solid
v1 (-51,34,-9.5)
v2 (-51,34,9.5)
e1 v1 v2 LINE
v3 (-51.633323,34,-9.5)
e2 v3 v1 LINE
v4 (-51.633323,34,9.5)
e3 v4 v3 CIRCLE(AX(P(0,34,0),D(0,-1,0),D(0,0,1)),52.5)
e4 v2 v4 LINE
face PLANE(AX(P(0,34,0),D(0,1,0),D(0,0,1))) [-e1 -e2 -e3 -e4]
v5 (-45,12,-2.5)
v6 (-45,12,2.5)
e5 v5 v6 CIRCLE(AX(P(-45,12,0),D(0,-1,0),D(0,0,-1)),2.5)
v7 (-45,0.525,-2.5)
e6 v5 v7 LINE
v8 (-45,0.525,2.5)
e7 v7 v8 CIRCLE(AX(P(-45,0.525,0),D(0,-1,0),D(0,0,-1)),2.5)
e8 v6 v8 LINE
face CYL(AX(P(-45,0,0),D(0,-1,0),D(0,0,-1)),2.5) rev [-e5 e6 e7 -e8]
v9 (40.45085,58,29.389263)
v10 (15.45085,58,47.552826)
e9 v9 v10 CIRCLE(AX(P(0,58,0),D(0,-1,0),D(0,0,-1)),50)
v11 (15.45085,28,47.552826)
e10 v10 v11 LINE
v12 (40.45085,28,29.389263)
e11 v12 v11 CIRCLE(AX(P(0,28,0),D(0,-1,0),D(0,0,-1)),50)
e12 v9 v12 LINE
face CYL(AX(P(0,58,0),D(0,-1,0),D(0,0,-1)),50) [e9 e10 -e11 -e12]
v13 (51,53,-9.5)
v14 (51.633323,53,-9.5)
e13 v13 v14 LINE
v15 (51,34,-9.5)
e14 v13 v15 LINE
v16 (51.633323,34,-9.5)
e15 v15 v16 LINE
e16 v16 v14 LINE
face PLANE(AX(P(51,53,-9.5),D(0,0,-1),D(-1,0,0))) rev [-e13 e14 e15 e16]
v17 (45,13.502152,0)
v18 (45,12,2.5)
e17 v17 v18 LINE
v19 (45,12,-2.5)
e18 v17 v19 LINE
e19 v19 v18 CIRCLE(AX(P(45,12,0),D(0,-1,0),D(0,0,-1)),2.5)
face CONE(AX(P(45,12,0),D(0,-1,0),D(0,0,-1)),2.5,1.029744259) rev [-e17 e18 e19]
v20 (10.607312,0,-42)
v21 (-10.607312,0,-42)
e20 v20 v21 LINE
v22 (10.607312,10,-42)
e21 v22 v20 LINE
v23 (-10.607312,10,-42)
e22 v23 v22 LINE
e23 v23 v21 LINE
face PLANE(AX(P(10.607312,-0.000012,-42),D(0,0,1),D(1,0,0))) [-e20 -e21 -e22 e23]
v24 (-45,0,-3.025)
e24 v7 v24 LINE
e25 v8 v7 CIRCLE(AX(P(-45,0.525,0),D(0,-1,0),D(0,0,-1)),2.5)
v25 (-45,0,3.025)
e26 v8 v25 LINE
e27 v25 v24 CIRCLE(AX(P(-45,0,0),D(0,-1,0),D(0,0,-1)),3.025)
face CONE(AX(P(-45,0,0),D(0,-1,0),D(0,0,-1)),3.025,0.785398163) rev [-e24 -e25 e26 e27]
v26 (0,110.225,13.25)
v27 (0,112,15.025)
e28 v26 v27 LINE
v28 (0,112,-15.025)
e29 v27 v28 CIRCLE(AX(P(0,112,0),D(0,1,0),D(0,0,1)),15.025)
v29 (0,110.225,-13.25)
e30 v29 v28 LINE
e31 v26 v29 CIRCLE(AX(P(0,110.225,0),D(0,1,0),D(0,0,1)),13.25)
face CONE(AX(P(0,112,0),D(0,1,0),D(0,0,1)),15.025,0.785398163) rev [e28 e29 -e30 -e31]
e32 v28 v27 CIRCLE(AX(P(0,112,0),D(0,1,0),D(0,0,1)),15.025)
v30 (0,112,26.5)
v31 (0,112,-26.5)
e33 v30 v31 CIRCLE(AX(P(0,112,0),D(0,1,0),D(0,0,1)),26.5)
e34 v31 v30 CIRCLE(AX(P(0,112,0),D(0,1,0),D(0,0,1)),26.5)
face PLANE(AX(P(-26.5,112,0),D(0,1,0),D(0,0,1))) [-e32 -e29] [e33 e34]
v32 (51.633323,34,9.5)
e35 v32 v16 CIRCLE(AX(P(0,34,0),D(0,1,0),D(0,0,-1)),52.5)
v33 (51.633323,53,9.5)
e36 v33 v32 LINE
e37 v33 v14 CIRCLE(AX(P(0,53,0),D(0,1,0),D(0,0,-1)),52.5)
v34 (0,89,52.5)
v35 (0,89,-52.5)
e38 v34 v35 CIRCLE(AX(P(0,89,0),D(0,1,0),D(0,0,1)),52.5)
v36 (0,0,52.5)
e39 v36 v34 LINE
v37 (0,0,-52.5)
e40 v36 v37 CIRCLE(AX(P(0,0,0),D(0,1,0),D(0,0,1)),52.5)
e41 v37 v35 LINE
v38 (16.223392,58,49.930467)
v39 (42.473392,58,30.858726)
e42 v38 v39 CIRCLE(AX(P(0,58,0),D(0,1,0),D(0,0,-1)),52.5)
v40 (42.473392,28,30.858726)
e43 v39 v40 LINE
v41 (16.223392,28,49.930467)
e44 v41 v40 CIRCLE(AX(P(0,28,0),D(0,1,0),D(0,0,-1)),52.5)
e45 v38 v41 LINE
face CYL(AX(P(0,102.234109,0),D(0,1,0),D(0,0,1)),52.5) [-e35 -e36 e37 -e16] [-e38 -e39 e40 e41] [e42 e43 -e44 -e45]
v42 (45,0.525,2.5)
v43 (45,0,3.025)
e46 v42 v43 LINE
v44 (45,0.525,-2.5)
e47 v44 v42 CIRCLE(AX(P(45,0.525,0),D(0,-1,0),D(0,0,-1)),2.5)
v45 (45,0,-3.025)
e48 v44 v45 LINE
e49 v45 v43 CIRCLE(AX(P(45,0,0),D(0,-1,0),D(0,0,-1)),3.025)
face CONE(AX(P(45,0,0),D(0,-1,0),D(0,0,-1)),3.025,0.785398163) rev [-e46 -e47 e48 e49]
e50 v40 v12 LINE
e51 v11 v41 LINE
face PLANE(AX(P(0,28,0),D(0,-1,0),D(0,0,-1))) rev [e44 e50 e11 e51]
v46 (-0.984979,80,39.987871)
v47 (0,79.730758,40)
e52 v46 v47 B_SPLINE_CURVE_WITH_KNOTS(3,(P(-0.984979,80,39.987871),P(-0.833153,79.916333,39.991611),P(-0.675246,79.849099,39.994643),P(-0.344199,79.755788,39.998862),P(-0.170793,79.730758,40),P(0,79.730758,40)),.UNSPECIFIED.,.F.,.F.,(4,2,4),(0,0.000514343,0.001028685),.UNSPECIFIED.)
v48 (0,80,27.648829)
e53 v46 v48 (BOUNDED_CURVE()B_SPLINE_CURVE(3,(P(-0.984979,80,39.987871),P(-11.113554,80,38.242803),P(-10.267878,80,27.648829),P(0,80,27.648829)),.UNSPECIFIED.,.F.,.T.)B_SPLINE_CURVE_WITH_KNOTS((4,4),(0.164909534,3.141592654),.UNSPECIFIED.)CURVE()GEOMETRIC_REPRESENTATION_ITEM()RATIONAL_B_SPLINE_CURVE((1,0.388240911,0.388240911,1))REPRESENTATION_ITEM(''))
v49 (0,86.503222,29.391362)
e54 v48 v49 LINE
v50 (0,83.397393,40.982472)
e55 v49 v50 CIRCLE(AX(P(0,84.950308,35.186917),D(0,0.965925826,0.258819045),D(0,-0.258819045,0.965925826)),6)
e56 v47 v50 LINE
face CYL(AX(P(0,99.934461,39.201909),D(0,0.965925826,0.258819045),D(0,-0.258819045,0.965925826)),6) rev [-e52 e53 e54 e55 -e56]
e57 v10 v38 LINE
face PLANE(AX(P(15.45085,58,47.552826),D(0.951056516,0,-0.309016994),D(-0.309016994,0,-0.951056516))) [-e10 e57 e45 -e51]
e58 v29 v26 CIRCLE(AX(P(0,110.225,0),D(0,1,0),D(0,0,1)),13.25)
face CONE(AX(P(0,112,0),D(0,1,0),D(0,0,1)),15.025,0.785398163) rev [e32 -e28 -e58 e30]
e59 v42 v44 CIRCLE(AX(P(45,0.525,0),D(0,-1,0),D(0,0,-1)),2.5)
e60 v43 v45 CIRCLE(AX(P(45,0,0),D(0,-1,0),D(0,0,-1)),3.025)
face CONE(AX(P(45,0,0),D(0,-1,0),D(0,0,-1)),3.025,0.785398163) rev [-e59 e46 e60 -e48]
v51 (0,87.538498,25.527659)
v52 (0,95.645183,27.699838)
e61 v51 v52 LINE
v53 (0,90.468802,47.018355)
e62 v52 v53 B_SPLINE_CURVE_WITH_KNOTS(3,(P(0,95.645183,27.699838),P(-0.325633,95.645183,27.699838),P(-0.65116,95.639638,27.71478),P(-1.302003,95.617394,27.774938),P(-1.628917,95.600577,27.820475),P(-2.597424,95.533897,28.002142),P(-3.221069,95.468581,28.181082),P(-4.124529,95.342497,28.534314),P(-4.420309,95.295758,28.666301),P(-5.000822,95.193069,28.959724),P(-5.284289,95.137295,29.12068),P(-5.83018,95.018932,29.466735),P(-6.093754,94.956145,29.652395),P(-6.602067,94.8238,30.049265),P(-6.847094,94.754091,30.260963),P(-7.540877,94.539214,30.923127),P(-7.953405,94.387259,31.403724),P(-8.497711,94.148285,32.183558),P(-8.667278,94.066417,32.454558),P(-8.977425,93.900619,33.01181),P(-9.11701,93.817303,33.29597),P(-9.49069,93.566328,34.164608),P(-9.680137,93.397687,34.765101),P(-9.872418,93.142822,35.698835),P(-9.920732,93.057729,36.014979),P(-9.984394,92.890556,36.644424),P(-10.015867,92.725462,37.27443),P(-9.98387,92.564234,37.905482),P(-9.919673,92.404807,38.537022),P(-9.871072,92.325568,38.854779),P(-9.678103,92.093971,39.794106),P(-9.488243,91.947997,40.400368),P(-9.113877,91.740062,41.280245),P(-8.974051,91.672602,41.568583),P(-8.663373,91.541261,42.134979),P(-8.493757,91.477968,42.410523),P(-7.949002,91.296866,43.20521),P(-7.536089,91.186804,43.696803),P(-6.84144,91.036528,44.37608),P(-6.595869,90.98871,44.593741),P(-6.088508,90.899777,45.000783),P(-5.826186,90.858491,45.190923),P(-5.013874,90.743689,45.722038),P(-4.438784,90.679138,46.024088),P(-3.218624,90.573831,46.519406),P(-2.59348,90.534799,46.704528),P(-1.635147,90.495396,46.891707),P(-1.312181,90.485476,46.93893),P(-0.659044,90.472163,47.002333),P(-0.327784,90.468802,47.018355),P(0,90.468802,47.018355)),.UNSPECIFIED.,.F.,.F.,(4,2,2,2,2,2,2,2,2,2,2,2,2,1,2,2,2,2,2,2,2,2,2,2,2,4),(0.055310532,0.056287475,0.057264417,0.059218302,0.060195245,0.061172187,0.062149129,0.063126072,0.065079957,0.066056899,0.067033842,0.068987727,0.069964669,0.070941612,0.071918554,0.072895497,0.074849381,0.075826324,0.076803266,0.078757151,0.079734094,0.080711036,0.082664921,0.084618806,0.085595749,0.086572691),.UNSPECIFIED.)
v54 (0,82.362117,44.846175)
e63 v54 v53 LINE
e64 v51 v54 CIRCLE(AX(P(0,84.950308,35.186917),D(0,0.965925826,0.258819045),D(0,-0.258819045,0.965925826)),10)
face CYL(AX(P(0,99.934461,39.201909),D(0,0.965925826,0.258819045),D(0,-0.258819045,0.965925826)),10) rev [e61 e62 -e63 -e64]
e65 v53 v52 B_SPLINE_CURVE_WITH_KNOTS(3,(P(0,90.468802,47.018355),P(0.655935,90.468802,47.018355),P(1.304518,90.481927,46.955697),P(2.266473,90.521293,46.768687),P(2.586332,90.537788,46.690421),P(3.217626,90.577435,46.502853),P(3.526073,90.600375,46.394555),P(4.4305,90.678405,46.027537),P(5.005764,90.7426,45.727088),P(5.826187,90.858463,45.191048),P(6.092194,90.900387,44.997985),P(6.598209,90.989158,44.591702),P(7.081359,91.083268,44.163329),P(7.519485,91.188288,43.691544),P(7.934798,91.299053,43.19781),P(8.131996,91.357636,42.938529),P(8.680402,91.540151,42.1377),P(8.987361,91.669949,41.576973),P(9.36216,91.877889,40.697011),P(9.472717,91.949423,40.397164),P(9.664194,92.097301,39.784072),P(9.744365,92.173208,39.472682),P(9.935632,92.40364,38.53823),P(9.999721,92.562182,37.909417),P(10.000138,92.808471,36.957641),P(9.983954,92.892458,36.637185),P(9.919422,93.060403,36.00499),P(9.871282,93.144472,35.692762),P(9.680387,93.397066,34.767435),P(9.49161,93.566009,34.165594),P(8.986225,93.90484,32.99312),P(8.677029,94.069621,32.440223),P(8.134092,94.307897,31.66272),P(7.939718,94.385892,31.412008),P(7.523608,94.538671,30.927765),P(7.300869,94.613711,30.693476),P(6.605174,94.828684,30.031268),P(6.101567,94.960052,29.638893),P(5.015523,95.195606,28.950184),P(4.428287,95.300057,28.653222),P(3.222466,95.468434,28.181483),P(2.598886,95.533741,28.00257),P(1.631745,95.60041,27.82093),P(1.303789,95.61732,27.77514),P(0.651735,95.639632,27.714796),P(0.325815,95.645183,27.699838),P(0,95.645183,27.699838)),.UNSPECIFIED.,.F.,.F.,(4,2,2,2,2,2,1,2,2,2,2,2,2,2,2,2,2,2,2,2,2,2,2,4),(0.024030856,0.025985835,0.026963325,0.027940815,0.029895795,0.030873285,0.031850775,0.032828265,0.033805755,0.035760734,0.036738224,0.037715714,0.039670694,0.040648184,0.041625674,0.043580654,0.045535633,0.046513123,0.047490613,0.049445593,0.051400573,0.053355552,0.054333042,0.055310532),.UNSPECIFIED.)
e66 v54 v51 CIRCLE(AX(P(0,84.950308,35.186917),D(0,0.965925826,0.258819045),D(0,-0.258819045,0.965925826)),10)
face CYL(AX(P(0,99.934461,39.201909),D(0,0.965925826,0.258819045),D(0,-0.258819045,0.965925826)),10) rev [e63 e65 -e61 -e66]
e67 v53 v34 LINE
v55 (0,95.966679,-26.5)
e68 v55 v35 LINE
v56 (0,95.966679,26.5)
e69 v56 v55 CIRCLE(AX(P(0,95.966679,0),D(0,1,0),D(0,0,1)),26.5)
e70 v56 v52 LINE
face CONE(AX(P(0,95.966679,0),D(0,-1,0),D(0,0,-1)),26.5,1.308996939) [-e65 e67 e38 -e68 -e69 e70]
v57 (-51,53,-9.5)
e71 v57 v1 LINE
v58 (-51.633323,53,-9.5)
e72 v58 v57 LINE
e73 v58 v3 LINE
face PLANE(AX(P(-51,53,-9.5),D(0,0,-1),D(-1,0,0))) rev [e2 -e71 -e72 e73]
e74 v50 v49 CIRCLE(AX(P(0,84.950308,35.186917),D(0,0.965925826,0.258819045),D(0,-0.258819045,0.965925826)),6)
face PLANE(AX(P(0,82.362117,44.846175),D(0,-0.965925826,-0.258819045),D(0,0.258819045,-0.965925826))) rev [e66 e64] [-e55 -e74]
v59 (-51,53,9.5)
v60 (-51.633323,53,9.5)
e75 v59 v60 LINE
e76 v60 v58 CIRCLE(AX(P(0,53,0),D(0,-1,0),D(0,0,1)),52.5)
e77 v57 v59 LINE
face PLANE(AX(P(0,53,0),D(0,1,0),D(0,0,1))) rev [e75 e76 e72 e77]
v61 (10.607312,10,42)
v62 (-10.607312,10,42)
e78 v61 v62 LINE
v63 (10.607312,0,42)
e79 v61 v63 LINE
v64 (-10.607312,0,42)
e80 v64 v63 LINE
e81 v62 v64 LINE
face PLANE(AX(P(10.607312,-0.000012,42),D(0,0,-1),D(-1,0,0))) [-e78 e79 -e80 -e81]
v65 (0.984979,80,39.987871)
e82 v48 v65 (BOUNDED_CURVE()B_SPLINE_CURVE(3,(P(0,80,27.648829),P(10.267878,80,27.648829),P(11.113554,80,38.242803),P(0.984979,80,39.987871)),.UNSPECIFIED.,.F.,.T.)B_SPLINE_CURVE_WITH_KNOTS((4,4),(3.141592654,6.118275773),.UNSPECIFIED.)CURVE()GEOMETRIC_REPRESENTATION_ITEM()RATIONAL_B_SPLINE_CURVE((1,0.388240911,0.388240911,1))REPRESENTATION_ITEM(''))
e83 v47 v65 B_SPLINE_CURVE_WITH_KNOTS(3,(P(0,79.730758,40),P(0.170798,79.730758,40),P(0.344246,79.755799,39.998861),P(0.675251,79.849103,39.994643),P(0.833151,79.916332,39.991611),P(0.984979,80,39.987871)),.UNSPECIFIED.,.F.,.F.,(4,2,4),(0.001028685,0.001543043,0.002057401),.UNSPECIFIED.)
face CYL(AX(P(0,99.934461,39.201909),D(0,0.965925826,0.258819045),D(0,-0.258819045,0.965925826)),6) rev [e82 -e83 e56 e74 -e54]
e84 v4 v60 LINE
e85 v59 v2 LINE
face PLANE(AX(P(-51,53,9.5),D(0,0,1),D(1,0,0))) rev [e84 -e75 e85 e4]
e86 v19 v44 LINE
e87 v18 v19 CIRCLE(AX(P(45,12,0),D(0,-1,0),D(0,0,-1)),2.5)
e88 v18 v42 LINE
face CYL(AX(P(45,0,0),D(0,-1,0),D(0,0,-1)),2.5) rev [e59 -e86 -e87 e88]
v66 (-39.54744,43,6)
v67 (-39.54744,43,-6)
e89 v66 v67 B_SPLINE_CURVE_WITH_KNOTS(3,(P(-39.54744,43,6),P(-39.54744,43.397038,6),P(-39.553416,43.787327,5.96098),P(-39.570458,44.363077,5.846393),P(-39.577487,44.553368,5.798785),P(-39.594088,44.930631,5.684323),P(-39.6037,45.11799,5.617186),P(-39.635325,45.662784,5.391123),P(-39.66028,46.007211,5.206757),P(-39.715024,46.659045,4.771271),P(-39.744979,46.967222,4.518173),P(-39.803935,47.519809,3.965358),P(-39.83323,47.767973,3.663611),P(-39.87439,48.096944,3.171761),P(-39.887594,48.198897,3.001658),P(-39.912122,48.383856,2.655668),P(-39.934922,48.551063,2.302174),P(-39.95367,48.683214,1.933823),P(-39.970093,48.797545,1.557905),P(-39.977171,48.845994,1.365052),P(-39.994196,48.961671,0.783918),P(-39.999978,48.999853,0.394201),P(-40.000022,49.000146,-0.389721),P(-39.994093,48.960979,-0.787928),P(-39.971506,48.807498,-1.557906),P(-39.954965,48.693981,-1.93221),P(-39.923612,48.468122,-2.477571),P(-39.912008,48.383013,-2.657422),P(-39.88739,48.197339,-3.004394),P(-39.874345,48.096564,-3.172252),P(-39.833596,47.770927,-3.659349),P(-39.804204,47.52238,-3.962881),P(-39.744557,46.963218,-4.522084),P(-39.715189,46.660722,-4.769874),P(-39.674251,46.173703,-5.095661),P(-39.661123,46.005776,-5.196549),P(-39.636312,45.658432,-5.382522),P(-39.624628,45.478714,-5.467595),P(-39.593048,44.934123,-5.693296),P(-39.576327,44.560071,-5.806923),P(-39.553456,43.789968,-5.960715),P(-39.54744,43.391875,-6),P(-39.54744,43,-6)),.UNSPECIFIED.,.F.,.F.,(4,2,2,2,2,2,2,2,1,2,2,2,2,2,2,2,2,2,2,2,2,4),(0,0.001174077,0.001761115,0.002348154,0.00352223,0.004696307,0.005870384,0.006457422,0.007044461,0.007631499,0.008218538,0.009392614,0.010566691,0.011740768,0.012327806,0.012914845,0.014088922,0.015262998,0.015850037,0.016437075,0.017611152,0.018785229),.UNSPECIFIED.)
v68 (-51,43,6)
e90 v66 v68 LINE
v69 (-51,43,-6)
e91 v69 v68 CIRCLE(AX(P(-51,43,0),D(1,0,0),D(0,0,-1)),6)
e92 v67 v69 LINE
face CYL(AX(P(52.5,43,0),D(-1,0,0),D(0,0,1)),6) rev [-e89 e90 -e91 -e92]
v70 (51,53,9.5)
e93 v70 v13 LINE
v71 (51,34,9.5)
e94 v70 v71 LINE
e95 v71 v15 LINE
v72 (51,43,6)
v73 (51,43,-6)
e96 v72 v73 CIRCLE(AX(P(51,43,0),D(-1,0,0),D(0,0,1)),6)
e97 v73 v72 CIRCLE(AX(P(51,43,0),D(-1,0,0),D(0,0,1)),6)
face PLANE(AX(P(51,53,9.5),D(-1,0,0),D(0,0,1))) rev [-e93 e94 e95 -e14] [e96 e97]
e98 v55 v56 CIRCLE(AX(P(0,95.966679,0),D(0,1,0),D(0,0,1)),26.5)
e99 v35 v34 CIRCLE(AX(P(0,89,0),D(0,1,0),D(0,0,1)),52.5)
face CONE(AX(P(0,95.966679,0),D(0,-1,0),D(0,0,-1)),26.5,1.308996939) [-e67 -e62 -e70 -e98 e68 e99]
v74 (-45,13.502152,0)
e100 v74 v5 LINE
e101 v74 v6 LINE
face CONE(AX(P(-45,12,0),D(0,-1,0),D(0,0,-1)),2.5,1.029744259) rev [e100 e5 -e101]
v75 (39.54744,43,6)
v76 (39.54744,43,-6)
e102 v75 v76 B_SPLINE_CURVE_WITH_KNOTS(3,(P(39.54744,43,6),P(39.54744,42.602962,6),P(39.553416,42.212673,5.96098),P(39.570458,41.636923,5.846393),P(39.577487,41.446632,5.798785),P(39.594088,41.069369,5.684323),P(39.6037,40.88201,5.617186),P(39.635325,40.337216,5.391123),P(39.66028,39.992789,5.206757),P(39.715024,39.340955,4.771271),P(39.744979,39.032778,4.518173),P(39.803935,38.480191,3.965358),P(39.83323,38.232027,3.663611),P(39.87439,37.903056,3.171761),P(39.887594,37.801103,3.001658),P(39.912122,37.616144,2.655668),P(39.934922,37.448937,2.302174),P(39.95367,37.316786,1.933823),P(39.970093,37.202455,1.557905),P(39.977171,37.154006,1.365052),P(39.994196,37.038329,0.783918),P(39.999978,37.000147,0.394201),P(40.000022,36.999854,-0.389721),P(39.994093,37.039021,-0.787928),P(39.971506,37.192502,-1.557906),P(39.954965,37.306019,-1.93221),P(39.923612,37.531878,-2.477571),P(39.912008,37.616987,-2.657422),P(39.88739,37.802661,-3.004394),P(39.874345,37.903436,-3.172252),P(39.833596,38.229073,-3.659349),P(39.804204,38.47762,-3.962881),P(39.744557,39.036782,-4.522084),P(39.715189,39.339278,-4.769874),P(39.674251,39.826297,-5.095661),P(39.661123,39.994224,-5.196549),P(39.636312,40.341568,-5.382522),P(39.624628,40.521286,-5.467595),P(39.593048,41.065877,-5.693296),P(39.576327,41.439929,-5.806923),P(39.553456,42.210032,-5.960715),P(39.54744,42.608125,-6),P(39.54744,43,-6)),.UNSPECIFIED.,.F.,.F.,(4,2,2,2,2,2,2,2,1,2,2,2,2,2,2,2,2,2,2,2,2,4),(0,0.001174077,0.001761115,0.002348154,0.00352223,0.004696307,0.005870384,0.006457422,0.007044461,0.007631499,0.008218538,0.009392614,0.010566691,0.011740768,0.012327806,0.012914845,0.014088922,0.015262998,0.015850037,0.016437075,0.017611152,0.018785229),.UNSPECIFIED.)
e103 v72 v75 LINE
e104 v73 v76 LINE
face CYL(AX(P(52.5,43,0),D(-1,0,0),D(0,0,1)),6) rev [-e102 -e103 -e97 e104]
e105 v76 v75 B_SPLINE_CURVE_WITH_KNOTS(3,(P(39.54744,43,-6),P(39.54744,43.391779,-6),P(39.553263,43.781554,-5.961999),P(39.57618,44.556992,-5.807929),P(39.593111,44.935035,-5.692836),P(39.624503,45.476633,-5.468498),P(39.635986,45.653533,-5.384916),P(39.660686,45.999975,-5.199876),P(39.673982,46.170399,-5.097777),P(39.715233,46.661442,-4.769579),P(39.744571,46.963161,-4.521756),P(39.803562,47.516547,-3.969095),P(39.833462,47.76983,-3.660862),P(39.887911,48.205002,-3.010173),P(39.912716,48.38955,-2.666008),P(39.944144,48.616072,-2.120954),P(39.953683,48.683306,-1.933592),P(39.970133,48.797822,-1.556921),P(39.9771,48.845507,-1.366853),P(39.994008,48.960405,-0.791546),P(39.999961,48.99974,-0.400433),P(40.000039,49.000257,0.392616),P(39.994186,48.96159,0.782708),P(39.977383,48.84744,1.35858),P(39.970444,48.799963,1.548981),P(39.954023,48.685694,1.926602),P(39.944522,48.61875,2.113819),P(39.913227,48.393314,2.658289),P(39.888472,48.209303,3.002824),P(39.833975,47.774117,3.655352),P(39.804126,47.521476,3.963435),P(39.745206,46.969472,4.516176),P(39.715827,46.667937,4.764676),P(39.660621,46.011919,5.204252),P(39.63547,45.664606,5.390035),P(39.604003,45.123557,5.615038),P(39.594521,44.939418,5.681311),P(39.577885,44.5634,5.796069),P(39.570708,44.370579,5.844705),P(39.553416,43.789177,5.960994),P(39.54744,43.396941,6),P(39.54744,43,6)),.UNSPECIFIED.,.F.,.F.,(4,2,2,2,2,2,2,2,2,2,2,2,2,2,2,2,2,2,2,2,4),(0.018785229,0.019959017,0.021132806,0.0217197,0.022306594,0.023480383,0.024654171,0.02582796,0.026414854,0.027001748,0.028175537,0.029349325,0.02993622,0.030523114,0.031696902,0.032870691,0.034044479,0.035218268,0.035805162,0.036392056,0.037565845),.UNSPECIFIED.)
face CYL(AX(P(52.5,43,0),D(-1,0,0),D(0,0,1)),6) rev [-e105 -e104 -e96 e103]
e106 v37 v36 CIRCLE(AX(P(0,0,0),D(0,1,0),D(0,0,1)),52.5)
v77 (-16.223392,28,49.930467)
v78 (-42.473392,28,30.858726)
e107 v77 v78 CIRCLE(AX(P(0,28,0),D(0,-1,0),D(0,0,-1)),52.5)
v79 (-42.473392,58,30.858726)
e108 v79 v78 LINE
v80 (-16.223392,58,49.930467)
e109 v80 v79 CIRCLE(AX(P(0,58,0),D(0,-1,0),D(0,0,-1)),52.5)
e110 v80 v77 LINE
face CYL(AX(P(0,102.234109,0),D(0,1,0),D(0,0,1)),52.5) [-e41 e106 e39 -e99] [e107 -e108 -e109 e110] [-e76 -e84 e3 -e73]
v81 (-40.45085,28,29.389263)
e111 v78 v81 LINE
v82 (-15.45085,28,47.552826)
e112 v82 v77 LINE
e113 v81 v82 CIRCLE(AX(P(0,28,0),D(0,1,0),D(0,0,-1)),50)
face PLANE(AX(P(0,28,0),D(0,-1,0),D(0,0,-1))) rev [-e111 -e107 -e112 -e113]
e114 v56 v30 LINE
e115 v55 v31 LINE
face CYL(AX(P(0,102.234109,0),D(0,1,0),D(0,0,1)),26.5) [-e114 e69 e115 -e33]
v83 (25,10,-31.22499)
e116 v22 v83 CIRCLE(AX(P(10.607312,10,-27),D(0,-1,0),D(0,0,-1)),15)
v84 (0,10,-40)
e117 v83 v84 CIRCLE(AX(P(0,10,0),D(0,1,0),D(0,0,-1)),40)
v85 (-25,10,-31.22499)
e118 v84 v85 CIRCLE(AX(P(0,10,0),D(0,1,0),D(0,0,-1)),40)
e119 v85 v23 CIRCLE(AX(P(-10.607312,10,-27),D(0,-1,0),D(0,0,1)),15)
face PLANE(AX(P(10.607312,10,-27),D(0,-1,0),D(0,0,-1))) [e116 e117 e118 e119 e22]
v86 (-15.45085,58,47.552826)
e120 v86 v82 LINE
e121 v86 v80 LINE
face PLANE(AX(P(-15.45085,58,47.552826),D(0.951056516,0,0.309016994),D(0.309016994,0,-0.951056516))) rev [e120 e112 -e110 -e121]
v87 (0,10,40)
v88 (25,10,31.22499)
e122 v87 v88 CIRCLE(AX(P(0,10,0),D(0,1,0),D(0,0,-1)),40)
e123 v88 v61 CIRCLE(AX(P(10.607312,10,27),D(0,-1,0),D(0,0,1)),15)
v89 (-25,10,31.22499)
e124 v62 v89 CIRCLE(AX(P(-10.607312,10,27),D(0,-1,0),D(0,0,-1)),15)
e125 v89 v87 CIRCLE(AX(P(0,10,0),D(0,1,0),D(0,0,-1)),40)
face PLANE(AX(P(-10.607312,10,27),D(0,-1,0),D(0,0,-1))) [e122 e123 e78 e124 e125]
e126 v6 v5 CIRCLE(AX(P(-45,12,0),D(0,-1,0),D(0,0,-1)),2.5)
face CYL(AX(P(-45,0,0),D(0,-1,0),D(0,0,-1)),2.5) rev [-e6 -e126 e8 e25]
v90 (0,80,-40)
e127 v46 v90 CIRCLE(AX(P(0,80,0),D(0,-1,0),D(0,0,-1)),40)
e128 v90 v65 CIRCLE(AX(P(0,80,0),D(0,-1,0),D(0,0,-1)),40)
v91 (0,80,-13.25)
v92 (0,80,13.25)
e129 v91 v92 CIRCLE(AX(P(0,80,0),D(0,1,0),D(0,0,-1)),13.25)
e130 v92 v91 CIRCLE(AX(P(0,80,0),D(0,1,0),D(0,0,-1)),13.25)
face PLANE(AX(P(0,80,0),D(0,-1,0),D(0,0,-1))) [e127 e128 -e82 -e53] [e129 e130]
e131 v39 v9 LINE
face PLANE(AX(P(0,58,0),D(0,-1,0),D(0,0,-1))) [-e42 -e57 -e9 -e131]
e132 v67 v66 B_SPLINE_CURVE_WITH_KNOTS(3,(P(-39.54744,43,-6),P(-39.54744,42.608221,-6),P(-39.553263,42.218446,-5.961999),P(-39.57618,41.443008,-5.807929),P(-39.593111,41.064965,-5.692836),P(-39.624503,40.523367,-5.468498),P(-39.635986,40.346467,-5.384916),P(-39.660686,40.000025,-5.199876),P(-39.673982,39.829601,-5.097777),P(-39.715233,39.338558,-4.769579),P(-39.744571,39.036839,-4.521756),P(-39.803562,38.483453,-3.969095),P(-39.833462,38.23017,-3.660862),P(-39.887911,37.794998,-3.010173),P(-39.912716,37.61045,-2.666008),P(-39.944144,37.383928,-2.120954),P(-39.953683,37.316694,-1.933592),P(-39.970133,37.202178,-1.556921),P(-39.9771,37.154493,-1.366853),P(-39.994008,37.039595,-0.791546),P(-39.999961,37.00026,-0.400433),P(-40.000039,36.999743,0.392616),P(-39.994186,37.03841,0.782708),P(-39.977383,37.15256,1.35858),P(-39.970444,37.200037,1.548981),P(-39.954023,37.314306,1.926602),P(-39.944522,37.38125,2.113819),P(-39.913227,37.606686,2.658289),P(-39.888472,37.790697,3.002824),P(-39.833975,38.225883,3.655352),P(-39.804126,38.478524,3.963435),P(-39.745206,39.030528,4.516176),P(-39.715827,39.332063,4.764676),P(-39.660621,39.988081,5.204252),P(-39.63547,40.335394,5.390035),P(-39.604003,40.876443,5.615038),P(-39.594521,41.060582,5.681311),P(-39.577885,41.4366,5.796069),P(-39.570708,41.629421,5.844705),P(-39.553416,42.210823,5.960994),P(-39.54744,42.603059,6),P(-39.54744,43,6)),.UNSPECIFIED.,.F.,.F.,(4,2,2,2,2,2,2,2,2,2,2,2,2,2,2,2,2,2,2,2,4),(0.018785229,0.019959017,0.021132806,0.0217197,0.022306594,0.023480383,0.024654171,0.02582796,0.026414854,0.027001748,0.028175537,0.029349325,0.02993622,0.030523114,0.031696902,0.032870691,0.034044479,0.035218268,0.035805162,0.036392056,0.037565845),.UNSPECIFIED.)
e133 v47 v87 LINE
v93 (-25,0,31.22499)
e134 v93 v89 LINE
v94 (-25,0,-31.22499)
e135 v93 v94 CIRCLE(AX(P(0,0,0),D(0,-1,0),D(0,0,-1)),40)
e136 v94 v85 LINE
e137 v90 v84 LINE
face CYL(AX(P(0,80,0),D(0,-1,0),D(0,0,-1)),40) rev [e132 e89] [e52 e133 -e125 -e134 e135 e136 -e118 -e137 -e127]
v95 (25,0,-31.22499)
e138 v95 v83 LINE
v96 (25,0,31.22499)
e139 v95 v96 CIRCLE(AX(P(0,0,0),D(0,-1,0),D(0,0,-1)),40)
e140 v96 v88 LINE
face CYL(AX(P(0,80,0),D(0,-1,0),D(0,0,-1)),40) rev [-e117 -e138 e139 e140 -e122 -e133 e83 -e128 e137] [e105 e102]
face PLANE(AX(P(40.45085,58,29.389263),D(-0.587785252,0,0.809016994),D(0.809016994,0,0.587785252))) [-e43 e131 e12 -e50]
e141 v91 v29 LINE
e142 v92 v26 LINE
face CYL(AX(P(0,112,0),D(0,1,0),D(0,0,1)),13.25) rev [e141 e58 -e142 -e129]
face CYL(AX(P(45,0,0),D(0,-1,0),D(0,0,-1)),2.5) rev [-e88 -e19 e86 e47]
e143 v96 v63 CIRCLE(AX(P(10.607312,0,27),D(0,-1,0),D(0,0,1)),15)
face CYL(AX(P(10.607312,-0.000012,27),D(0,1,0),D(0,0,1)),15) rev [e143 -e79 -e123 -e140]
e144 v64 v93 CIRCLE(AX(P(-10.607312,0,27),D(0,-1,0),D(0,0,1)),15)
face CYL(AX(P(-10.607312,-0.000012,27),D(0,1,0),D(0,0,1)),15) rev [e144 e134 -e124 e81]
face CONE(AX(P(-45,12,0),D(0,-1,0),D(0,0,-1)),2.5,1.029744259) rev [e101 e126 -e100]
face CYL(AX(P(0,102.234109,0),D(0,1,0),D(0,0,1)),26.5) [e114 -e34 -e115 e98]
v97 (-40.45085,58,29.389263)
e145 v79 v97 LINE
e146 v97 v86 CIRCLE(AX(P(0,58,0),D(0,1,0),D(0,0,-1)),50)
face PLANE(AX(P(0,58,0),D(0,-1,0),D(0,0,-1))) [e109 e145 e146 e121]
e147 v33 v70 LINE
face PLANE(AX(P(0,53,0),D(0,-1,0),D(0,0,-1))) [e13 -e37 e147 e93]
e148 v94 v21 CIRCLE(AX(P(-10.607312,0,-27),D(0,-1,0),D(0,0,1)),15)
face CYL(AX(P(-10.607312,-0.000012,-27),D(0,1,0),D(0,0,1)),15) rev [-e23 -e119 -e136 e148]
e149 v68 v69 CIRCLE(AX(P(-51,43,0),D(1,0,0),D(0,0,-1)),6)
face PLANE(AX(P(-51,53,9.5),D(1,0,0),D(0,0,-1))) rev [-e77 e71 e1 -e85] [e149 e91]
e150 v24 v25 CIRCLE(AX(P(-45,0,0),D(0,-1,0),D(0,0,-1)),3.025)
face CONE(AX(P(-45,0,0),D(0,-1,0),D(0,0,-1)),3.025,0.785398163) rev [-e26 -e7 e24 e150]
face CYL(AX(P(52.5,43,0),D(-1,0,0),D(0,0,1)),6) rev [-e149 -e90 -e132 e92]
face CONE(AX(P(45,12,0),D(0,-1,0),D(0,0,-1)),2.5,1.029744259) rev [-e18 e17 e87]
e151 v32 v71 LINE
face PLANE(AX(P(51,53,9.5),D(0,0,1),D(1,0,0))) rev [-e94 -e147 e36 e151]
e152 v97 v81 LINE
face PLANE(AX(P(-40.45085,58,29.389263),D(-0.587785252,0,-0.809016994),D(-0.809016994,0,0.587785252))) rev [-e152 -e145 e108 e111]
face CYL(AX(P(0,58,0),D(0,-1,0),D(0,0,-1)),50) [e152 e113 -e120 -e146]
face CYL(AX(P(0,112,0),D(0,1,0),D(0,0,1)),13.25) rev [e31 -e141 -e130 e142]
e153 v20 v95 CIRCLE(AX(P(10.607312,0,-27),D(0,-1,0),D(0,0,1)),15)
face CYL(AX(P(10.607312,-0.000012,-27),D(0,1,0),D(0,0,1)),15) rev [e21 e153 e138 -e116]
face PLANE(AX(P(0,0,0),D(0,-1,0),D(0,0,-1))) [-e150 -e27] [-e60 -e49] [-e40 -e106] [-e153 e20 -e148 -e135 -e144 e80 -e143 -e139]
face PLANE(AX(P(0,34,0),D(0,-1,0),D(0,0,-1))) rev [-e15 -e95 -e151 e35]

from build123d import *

# Parameters (mm, degrees)
M30_TAPPED_HOLE1_D           = 26.5
M30_TAPPED_HOLE1_DEPTH       = 77.5
M30_TAPPED_HOLE1_CSINK_D     = 30.05
M30_TAPPED_HOLE1_CSINK_ANGLE = 90
M30_TAPPED_HOLE1_TIP         = 7.961403202
SKETCH6_R                    = 40
CUT_EXTRUDE1_DEPTH           = 80
CUT_EXTRUDE2_START           = -43
CUT_EXTRUDE2_DEPTH           = 15
M6_TAPPED_HOLE1_D            = 5
M6_TAPPED_HOLE1_DEPTH        = 12
M6_TAPPED_HOLE1_CSINK_D      = 6.05
M6_TAPPED_HOLE1_CSINK_ANGLE  = 90
M6_TAPPED_HOLE1_TIP          = 1.502151548
CUT_EXTRUDE3_START           = -43.5
SKETCH14_W                   = 3
SKETCH14_H                   = 19
CUT_EXTRUDE3_DEPTH           = 9.5
CUT_EXTRUDE4_DEPTH           = 162.283911163
CUT_EXTRUDE4_DEPTH_BACK      = 162.283911163
SKETCH15_R                   = 6
CUT_EXTRUDE5_DEPTH           = 135.374476743
CUT_EXTRUDE5_DEPTH_BACK      = 10


with BuildPart() as part:
    # Sketch2 → Revolve1 (revolve)
    with BuildSketch(Plane.XY, mode=Mode.PRIVATE) as revolve1_sk:
        Polygon((0, 0), (0, 112), (-26.5, 112), (-26.5, 95.966679003), (-52.5, 89), (-52.5, 0), align=None)
    revolve(revolve1_sk.sketch.rotate(Axis((0, 102.234109067, 0), (0, -1, 0)), 270), axis=Axis((0, 102.234109067, 0), (0, -1, 0)))

    # M30 Tapped Hole1
    with Locations(Plane(origin=(0, 112, 0), x_dir=(1, 0, 0), z_dir=(0, 1, 0))):
        with Locations((0, 0)):
            CounterSinkHole(M30_TAPPED_HOLE1_D / 2, M30_TAPPED_HOLE1_CSINK_D / 2, depth=M30_TAPPED_HOLE1_DEPTH, counter_sink_angle=M30_TAPPED_HOLE1_CSINK_ANGLE)
            with Locations((0, 0, -(M30_TAPPED_HOLE1_DEPTH + M30_TAPPED_HOLE1_TIP / 2))):  # 118° drill point
                Cone(0, M30_TAPPED_HOLE1_D / 2, M30_TAPPED_HOLE1_TIP, mode=Mode.SUBTRACT)

    # Sketch6 → Cut-Extrude1 (cut)
    with BuildSketch(Plane.XZ):
        with Locations(Location((0, 0, 0), (0, 0, 270))):
            Circle(SKETCH6_R)
    extrude(amount=-CUT_EXTRUDE1_DEPTH, mode=Mode.SUBTRACT)

    # Sketch8 → Cut-Extrude2 (cut, symmetric)
    with BuildSketch(Plane.XZ.offset(CUT_EXTRUDE2_START)):
        with BuildLine():
            Line((-15.450849719, 47.552825815), (-16.223392205, 49.930467105))
            ThreePointArc((-16.223392205, 49.930467105), (-30.858725745, 42.473392205), (-42.473392205, 30.858725745))
            Line((-42.473392205, 30.858725745), (-40.450849719, 29.389262615))
            ThreePointArc((-40.450849719, 29.389262615), (-29.389262615, 40.450849719), (-15.450849719, 47.552825815))
        make_face()
    cut_extrude2 = extrude(amount=CUT_EXTRUDE2_DEPTH, both=True, mode=Mode.SUBTRACT)

    # Mirror1: Cut-Extrude2 across plane
    add(cut_extrude2.mirror(Plane(origin=(0, 0, 0), x_dir=(0, 0, 1), z_dir=(1, 0, 0))), mode=Mode.SUBTRACT)

    # M6 Tapped Hole1
    with Locations(Plane.XZ):
        with Locations((-45, 0), (45, 0)):
            CounterSinkHole(M6_TAPPED_HOLE1_D / 2, M6_TAPPED_HOLE1_CSINK_D / 2, depth=M6_TAPPED_HOLE1_DEPTH, counter_sink_angle=M6_TAPPED_HOLE1_CSINK_ANGLE)
            with Locations((0, 0, -(M6_TAPPED_HOLE1_DEPTH + M6_TAPPED_HOLE1_TIP / 2))):  # 118° drill point
                Cone(0, M6_TAPPED_HOLE1_D / 2, M6_TAPPED_HOLE1_TIP, mode=Mode.SUBTRACT)

    # Sketch14 → Cut-Extrude3 (cut, symmetric)
    with BuildSketch(Plane.XZ.offset(CUT_EXTRUDE3_START)):
        with Locations((52.5, 0)):
            Rectangle(SKETCH14_W, SKETCH14_H)
        with Locations((-52.5, 0)):
            Rectangle(SKETCH14_W, SKETCH14_H)
    extrude(amount=CUT_EXTRUDE3_DEPTH, both=True, mode=Mode.SUBTRACT)

    # Sketch15 → Cut-Extrude4 (cut, two sides: drawn at the far end of the back side and taken through both)
    with BuildSketch(Plane.ZY.offset(51).offset(-CUT_EXTRUDE4_DEPTH_BACK)):
        with Locations((0, 43)):
            Circle(SKETCH15_R)
    extrude(amount=CUT_EXTRUDE4_DEPTH + CUT_EXTRUDE4_DEPTH_BACK, mode=Mode.SUBTRACT)

    # Sketch16 → Cut-Extrude5 (cut, two sides: drawn at the far end of the back side and taken through both)
    with BuildSketch(Plane.XZ.offset(-CUT_EXTRUDE5_DEPTH_BACK)):
        with BuildLine():
            Line((10.607312288, 42), (-10.607312288, 42))
            ThreePointArc((-10.607312288, 42), (-19.596893761, 39.007806833), (-25, 31.224989992))
            ThreePointArc((-25, 31.224989992), (0, 40), (25, 31.224989992))
            ThreePointArc((25, 31.224989992), (19.596893761, 39.007806833), (10.607312288, 42))
        make_face()
        with BuildLine():
            Line((10.607312288, -42), (-10.607312288, -42))
            ThreePointArc((-10.607312288, -42), (-19.596893761, -39.007806833), (-25, -31.224989992))
            ThreePointArc((-25, -31.224989992), (0, -40), (25, -31.224989992))
            ThreePointArc((25, -31.224989992), (19.596893761, -39.007806833), (10.607312288, -42))
        make_face()
    extrude(amount=CUT_EXTRUDE5_DEPTH + CUT_EXTRUDE5_DEPTH_BACK, mode=Mode.SUBTRACT)

    # Sketch17 → Cut-Revolve4 (revolve, cut)
    with BuildSketch(Plane(origin=(0, 0, 0), x_dir=(0, 0, -1), z_dir=(1, 0, 0))):
        Polygon((-37.77510745, 94.609566001), (-47.434365712, 92.02137555), (-44.846175261, 82.362117287), (-40.982471956, 83.397393467), (-38.749196282, 75.062695183), (-32.953641324, 76.615609453), align=None)
    revolve(axis=Axis((0, 99.934460592, 39.201908655), (0, -0.96592582628907, -0.2588190451025148)), mode=Mode.SUBTRACT)


solid = part.part
